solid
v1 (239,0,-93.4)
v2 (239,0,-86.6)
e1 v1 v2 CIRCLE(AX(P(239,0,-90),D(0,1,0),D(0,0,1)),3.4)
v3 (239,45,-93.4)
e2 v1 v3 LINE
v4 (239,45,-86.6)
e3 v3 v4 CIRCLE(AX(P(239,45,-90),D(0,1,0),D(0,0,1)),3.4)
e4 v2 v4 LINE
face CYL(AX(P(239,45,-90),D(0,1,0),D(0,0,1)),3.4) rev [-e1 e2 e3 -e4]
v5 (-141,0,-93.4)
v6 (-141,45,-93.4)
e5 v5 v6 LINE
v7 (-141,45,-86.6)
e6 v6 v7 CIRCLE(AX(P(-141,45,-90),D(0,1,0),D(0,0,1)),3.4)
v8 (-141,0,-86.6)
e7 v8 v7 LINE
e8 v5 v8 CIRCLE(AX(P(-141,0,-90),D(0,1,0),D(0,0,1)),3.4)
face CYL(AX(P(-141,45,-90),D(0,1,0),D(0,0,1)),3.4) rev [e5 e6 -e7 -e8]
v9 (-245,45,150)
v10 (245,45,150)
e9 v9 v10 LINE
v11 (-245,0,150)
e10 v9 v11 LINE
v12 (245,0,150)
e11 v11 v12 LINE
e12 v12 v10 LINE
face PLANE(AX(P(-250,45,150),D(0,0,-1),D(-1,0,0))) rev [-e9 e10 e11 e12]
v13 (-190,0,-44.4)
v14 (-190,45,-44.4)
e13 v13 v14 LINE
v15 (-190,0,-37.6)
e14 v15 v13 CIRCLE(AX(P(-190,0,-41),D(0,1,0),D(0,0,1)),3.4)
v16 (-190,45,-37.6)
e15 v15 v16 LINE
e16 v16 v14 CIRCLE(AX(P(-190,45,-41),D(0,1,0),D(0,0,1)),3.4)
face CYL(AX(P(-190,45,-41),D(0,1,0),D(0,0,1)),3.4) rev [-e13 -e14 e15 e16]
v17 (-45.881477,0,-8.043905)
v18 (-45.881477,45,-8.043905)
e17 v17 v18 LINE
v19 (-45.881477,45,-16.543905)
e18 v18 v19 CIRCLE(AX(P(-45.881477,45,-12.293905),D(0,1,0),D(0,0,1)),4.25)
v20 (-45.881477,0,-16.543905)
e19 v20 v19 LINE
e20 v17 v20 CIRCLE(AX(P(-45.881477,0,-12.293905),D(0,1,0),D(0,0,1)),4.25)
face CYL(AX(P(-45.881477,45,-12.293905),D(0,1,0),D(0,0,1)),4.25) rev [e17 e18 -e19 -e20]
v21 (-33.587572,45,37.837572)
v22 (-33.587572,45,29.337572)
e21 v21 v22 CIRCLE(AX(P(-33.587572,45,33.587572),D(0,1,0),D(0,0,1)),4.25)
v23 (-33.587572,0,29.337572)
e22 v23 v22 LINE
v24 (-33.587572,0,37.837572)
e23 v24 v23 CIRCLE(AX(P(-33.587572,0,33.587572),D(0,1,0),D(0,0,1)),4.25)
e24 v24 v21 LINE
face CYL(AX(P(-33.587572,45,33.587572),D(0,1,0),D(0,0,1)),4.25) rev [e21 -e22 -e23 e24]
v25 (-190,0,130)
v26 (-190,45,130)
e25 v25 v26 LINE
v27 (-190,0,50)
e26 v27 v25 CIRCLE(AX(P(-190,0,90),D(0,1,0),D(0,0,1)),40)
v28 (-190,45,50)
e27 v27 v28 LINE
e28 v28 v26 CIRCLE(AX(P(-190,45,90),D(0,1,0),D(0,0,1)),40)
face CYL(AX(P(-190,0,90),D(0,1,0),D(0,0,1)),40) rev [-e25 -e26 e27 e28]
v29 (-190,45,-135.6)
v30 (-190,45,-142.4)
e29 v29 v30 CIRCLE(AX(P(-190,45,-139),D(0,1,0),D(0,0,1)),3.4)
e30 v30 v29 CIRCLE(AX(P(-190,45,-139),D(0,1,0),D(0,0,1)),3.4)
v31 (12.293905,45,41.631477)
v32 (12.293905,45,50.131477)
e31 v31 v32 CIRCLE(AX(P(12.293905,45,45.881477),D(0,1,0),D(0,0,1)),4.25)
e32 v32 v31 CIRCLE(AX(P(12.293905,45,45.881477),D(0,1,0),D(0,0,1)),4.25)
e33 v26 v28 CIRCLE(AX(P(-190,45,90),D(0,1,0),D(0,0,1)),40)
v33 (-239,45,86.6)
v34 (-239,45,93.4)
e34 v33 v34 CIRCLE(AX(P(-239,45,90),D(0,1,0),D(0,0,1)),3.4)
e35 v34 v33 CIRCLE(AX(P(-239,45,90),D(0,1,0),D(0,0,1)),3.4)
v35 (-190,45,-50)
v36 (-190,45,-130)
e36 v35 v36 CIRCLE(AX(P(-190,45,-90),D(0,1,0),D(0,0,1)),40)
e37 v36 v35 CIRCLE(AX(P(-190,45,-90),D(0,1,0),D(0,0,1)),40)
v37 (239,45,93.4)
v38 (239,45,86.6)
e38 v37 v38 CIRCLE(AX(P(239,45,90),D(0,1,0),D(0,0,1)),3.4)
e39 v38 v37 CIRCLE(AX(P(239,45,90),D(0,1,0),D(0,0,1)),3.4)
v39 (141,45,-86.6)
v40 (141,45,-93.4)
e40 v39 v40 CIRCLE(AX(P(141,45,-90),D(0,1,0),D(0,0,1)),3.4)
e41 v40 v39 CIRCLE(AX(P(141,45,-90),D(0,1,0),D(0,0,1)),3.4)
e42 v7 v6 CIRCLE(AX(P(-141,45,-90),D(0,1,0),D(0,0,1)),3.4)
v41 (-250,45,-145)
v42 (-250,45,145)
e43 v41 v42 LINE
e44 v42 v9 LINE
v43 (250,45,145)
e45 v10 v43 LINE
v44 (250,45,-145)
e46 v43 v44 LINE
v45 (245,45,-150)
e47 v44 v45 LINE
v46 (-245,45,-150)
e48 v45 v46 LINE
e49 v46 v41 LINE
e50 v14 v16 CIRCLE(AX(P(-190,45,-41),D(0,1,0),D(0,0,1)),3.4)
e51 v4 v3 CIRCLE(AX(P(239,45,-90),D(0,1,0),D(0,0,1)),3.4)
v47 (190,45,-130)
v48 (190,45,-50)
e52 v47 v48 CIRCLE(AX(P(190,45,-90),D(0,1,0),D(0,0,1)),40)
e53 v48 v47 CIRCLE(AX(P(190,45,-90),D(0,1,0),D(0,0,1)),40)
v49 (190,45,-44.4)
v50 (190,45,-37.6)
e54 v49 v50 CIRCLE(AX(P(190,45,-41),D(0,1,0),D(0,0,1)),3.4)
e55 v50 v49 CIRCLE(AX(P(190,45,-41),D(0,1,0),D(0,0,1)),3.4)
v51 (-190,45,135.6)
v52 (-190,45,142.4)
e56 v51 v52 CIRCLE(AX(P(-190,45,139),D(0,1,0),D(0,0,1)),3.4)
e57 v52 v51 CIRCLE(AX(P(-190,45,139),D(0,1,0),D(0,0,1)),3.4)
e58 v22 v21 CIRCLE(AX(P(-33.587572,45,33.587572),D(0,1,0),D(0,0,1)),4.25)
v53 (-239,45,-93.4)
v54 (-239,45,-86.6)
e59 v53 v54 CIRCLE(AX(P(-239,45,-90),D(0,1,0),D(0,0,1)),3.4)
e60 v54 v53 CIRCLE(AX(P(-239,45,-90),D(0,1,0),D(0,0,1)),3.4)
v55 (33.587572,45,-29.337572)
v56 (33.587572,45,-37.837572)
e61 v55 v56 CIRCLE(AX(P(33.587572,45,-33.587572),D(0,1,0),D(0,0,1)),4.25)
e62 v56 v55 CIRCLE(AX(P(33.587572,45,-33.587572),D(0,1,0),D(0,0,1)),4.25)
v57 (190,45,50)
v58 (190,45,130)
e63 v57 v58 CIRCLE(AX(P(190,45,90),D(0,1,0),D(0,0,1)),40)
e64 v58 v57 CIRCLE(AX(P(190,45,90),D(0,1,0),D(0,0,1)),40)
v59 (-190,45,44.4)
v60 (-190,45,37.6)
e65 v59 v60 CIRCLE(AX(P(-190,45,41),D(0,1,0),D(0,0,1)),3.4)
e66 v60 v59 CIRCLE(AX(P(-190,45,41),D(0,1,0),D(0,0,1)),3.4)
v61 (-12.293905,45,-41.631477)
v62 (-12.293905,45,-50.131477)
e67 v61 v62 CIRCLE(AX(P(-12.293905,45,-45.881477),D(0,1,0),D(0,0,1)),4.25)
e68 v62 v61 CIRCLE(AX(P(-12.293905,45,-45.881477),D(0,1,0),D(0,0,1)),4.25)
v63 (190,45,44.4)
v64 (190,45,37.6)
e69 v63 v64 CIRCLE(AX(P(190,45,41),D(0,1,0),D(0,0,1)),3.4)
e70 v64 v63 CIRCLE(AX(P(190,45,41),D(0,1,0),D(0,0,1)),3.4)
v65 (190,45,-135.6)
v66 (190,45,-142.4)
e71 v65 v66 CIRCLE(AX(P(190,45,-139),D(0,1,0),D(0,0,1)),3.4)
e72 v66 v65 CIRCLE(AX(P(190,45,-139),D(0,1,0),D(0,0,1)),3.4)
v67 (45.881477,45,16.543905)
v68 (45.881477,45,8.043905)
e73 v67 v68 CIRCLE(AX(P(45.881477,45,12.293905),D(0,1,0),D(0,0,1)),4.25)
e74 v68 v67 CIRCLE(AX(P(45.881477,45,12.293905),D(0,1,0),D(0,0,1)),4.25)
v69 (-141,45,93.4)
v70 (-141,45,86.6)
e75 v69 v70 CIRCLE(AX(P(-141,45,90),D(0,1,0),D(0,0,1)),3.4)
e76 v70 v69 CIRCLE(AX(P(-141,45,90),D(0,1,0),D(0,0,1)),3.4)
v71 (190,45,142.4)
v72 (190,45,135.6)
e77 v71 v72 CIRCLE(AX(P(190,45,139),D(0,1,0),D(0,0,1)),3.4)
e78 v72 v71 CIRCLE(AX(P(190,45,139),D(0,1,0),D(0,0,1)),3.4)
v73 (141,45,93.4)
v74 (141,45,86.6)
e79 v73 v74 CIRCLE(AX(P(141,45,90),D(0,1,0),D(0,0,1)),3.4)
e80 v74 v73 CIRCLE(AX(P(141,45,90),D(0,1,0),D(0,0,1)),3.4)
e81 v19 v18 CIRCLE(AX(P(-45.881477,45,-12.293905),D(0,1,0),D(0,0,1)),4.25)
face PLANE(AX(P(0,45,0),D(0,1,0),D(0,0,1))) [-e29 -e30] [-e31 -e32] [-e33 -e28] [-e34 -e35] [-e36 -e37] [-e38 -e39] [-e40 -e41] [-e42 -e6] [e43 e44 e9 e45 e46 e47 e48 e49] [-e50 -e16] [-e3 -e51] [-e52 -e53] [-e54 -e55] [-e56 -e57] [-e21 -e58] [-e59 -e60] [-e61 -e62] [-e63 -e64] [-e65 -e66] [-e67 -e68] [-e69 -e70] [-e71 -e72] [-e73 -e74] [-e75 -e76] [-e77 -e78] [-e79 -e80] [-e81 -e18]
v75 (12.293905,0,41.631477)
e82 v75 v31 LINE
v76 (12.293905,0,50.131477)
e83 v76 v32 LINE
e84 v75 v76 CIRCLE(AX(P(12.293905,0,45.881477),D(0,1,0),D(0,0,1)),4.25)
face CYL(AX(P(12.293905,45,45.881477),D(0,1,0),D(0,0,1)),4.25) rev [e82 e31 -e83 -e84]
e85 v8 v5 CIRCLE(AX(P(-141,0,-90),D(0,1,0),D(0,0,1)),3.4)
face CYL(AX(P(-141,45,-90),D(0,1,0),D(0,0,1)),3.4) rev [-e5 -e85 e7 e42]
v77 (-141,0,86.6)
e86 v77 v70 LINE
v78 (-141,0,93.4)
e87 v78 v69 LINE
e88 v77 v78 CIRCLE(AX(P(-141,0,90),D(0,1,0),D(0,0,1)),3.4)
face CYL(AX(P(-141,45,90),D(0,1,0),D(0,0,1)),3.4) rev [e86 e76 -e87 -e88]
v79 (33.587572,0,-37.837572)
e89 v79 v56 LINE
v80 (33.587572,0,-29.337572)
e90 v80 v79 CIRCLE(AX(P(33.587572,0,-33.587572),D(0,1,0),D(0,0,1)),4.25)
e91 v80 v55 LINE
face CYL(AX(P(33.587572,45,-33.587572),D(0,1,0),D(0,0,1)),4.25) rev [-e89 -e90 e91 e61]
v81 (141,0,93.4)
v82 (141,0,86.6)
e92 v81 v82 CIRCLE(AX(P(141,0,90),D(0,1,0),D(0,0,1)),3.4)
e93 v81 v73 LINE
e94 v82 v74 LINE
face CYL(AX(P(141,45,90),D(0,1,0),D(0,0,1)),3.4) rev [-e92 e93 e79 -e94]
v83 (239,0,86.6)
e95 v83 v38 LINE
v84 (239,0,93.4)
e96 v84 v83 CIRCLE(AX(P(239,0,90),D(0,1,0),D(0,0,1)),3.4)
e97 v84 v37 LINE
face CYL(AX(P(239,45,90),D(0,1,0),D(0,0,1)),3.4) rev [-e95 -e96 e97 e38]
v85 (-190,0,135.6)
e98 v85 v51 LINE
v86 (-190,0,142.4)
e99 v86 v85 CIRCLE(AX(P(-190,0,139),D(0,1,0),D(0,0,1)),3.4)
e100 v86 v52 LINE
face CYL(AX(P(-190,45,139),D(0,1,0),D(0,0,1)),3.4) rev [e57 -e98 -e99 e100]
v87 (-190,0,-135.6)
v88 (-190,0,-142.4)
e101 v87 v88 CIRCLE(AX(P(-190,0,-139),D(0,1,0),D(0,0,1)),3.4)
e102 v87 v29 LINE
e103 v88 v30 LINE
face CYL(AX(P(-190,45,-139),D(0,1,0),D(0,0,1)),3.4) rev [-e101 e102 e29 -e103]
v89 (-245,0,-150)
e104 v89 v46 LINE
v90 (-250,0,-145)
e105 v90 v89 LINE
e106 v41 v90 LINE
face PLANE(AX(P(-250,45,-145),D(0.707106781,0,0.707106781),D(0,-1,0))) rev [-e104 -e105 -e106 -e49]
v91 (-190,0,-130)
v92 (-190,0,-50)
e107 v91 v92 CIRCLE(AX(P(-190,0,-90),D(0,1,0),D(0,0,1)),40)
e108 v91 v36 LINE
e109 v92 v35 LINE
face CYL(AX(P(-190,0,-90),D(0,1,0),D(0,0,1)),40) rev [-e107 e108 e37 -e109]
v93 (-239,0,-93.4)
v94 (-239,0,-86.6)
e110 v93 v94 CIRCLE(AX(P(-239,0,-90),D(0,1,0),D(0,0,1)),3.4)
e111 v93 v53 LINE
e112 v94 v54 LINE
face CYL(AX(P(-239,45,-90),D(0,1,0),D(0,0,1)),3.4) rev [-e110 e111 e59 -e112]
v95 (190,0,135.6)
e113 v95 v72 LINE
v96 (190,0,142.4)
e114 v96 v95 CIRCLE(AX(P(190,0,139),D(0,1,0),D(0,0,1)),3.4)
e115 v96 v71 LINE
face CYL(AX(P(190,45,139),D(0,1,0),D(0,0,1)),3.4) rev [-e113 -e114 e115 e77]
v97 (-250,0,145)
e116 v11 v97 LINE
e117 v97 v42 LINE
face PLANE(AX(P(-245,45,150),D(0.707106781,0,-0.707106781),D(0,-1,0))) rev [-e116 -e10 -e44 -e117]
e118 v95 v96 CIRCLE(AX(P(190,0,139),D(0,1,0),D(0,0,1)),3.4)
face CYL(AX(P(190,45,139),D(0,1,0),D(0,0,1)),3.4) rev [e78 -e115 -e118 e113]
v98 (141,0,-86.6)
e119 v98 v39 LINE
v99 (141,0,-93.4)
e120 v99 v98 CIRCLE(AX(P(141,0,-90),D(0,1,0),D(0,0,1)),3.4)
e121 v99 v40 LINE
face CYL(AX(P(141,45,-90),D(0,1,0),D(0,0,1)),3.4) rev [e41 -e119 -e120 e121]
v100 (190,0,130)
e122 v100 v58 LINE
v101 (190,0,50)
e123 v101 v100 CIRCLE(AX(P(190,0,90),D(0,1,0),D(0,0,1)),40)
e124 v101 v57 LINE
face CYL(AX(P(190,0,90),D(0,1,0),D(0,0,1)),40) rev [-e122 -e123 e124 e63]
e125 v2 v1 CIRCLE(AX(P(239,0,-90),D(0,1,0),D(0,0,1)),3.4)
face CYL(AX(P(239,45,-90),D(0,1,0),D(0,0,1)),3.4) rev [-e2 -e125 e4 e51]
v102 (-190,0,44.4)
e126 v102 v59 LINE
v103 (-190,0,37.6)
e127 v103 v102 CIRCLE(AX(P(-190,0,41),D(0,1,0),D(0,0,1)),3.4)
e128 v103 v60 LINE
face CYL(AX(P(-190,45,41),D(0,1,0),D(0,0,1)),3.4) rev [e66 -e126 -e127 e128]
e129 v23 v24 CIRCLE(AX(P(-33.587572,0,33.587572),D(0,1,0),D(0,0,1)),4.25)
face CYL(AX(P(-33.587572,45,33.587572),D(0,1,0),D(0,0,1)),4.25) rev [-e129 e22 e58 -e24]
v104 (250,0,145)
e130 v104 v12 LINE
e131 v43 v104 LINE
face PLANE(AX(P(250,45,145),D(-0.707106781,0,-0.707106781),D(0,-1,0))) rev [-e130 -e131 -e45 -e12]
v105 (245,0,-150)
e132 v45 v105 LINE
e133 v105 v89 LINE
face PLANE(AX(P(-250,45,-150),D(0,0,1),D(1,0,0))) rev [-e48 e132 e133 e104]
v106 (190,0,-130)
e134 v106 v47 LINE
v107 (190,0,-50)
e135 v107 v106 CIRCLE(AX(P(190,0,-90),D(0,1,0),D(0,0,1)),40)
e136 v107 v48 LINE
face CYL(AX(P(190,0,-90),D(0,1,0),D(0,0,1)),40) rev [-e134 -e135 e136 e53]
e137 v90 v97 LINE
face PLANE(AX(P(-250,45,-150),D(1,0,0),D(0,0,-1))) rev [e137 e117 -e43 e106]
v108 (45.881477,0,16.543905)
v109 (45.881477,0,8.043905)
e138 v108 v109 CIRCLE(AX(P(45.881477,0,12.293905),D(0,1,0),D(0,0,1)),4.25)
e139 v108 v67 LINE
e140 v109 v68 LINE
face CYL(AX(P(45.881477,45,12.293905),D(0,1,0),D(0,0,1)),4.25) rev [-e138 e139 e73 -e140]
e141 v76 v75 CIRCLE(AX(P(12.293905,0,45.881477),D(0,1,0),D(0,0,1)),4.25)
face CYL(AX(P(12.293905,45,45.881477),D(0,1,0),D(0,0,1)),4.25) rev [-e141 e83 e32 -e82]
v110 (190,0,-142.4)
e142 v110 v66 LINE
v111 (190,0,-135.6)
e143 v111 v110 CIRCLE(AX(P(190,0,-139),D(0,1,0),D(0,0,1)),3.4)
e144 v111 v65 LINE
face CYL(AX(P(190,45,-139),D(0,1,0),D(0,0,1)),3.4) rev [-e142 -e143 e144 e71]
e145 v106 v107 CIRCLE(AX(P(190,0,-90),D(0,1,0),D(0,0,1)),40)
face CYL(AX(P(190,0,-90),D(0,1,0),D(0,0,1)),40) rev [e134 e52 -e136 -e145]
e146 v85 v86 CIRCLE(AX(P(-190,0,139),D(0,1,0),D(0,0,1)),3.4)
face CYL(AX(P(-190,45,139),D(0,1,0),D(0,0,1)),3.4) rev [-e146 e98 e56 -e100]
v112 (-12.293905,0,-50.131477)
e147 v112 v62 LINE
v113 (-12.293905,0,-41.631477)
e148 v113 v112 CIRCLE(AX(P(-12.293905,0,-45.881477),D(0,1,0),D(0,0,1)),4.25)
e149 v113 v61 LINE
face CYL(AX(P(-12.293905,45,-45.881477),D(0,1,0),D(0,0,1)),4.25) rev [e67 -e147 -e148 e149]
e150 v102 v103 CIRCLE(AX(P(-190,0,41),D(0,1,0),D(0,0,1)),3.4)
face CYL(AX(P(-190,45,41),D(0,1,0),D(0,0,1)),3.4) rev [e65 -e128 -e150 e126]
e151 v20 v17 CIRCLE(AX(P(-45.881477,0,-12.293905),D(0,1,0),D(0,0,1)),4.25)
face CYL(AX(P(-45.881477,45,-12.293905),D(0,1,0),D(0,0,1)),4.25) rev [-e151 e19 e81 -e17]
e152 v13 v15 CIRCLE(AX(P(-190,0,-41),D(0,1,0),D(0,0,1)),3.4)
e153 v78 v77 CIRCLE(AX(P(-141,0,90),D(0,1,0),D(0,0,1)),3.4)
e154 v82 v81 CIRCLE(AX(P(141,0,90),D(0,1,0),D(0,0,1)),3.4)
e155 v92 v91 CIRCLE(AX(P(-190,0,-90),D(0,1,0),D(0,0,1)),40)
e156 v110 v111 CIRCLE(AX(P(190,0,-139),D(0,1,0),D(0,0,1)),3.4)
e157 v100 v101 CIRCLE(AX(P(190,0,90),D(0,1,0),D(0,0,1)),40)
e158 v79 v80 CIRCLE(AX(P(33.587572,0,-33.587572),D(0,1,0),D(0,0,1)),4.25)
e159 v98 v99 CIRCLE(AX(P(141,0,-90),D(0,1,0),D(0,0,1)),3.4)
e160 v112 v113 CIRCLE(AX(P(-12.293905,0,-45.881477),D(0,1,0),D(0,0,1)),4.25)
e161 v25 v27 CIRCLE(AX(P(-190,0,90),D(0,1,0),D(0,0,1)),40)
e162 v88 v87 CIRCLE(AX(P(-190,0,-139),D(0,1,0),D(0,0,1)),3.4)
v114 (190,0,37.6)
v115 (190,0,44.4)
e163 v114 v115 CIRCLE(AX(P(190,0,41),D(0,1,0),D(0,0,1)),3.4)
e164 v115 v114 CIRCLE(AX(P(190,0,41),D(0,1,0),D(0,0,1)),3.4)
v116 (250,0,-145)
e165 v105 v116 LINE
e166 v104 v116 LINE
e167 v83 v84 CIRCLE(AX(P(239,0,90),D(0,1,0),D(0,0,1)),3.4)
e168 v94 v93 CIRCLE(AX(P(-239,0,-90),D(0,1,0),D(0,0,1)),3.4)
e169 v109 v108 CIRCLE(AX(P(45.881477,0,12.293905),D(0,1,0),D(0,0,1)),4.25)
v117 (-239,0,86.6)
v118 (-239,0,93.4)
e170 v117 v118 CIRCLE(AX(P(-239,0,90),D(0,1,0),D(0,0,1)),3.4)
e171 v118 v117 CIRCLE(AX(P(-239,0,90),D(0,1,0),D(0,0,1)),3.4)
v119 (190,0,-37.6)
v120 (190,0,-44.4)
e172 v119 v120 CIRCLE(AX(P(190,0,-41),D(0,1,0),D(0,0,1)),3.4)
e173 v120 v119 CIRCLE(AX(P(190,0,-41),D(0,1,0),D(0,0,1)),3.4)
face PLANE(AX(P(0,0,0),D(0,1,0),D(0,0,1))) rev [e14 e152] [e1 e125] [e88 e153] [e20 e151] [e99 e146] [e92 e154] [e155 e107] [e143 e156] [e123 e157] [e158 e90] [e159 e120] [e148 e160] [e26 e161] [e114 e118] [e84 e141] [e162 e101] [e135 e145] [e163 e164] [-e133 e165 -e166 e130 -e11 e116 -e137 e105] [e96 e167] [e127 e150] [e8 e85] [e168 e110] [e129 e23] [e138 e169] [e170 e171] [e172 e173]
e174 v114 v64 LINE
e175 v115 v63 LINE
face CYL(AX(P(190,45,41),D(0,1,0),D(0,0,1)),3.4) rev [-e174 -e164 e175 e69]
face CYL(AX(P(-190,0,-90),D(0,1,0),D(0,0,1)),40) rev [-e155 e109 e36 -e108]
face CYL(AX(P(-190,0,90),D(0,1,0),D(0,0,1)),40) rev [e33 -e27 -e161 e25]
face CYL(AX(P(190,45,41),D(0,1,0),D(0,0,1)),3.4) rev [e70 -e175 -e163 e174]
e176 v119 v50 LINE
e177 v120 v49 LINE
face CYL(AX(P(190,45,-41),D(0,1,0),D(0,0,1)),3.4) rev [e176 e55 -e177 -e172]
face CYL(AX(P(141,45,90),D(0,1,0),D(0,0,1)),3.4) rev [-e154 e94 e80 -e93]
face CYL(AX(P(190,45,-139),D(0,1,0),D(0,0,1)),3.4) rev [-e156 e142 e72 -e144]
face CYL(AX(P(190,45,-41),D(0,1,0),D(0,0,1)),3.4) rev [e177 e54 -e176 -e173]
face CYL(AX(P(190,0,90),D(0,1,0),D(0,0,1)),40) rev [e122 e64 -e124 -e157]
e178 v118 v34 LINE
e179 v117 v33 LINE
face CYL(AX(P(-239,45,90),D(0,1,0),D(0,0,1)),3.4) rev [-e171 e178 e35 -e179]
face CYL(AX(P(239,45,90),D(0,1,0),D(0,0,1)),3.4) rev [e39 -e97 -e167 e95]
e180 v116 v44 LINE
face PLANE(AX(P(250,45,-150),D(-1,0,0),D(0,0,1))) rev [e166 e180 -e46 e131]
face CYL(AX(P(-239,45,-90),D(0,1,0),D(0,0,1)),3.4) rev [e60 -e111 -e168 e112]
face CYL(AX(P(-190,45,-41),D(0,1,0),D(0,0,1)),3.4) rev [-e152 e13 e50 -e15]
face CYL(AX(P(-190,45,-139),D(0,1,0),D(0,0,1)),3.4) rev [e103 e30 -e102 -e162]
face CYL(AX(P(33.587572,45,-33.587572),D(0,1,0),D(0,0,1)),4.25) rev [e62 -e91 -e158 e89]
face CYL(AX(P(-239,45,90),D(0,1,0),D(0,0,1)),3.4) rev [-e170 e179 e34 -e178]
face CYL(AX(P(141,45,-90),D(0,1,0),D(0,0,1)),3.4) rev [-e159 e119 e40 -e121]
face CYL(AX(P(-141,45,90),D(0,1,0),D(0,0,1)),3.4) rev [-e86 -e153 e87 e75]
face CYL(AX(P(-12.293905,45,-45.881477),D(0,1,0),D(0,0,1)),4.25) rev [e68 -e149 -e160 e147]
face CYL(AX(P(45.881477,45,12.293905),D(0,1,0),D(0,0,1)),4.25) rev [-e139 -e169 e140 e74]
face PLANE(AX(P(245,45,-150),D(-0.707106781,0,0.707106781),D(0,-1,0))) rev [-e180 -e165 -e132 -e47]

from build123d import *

# Parameters (mm, degrees)
SKETCH_1_W          = 500
SKETCH_1_H          = 300
EXTRUDE_1_DEPTH     = 45
CHAMFER_1_SIZE      = 5
SKETCH_6_R          = 40
CUT_EXTRUDE_1_DEPTH = 296
HOLE_WIZARD_M10_3_D = 8.5
HOLE_WIZARD_M8_1_D  = 6.8


with BuildPart() as part:
    # 草图1 → 凸台-拉伸1 (new body)
    with BuildSketch(Plane(origin=(0, 0, 0), x_dir=(1, 0, 0), z_dir=(0, 1, 0))):
        Rectangle(SKETCH_1_W, SKETCH_1_H)
    extrude(amount=EXTRUDE_1_DEPTH)

    # 倒角1
    chamfer_1_edges = [part.edges().sort_by_distance(p)[0] for p in [
        (250, 22.5, 150),
        (-250, 22.5, 150),
        (-250, 22.5, -150),
        (250, 22.5, -150),
    ]]
    chamfer(chamfer_1_edges, length=CHAMFER_1_SIZE)

    # 草图6 → 切除-拉伸1 (cut, through all)
    with BuildSketch(Plane(origin=(0, 45, 0), x_dir=(1, 0, 0), z_dir=(0, 1, 0))):
        with Locations(Location((190, -90, 0), (0, 0, 270))):
            Circle(SKETCH_6_R)
        with Locations(Location((190, 90, 0), (0, 0, 270))):
            Circle(SKETCH_6_R)
        with Locations(Location((-190, 90, 0), (0, 0, 270))):
            Circle(SKETCH_6_R)
        with Locations(Location((-190, -90, 0), (0, 0, 270))):
            Circle(SKETCH_6_R)
    extrude(amount=-CUT_EXTRUDE_1_DEPTH, mode=Mode.SUBTRACT)

    # M10 螺纹孔3 (through all)
    with Locations(Plane(origin=(0, 45, 0), x_dir=(1, 0, 0), z_dir=(0, 1, 0))):
        with Locations((-12.293904642, 45.881476749), (-45.881476749, 12.293904642), (-33.587572106, -33.587572106), (12.293904642, -45.881476749), (45.881476749, -12.293904642), (33.587572106, 33.587572106)):
            Hole(HOLE_WIZARD_M10_3_D / 2)

    # M8 螺纹孔1 (through all)
    with Locations(Plane(origin=(0, 45, 0), x_dir=(1, 0, 0), z_dir=(0, 1, 0))):
        with Locations((239, -90), (190, -139), (141, -90), (190, -41), (239, 90), (190, 41), (141, 90), (190, 139), (-141, -90), (-190, -139), (-239, -90), (-190, -41), (-141, 90), (-190, 41), (-239, 90), (-190, 139)):
            Hole(HOLE_WIZARD_M8_1_D / 2)


solid = part.part
